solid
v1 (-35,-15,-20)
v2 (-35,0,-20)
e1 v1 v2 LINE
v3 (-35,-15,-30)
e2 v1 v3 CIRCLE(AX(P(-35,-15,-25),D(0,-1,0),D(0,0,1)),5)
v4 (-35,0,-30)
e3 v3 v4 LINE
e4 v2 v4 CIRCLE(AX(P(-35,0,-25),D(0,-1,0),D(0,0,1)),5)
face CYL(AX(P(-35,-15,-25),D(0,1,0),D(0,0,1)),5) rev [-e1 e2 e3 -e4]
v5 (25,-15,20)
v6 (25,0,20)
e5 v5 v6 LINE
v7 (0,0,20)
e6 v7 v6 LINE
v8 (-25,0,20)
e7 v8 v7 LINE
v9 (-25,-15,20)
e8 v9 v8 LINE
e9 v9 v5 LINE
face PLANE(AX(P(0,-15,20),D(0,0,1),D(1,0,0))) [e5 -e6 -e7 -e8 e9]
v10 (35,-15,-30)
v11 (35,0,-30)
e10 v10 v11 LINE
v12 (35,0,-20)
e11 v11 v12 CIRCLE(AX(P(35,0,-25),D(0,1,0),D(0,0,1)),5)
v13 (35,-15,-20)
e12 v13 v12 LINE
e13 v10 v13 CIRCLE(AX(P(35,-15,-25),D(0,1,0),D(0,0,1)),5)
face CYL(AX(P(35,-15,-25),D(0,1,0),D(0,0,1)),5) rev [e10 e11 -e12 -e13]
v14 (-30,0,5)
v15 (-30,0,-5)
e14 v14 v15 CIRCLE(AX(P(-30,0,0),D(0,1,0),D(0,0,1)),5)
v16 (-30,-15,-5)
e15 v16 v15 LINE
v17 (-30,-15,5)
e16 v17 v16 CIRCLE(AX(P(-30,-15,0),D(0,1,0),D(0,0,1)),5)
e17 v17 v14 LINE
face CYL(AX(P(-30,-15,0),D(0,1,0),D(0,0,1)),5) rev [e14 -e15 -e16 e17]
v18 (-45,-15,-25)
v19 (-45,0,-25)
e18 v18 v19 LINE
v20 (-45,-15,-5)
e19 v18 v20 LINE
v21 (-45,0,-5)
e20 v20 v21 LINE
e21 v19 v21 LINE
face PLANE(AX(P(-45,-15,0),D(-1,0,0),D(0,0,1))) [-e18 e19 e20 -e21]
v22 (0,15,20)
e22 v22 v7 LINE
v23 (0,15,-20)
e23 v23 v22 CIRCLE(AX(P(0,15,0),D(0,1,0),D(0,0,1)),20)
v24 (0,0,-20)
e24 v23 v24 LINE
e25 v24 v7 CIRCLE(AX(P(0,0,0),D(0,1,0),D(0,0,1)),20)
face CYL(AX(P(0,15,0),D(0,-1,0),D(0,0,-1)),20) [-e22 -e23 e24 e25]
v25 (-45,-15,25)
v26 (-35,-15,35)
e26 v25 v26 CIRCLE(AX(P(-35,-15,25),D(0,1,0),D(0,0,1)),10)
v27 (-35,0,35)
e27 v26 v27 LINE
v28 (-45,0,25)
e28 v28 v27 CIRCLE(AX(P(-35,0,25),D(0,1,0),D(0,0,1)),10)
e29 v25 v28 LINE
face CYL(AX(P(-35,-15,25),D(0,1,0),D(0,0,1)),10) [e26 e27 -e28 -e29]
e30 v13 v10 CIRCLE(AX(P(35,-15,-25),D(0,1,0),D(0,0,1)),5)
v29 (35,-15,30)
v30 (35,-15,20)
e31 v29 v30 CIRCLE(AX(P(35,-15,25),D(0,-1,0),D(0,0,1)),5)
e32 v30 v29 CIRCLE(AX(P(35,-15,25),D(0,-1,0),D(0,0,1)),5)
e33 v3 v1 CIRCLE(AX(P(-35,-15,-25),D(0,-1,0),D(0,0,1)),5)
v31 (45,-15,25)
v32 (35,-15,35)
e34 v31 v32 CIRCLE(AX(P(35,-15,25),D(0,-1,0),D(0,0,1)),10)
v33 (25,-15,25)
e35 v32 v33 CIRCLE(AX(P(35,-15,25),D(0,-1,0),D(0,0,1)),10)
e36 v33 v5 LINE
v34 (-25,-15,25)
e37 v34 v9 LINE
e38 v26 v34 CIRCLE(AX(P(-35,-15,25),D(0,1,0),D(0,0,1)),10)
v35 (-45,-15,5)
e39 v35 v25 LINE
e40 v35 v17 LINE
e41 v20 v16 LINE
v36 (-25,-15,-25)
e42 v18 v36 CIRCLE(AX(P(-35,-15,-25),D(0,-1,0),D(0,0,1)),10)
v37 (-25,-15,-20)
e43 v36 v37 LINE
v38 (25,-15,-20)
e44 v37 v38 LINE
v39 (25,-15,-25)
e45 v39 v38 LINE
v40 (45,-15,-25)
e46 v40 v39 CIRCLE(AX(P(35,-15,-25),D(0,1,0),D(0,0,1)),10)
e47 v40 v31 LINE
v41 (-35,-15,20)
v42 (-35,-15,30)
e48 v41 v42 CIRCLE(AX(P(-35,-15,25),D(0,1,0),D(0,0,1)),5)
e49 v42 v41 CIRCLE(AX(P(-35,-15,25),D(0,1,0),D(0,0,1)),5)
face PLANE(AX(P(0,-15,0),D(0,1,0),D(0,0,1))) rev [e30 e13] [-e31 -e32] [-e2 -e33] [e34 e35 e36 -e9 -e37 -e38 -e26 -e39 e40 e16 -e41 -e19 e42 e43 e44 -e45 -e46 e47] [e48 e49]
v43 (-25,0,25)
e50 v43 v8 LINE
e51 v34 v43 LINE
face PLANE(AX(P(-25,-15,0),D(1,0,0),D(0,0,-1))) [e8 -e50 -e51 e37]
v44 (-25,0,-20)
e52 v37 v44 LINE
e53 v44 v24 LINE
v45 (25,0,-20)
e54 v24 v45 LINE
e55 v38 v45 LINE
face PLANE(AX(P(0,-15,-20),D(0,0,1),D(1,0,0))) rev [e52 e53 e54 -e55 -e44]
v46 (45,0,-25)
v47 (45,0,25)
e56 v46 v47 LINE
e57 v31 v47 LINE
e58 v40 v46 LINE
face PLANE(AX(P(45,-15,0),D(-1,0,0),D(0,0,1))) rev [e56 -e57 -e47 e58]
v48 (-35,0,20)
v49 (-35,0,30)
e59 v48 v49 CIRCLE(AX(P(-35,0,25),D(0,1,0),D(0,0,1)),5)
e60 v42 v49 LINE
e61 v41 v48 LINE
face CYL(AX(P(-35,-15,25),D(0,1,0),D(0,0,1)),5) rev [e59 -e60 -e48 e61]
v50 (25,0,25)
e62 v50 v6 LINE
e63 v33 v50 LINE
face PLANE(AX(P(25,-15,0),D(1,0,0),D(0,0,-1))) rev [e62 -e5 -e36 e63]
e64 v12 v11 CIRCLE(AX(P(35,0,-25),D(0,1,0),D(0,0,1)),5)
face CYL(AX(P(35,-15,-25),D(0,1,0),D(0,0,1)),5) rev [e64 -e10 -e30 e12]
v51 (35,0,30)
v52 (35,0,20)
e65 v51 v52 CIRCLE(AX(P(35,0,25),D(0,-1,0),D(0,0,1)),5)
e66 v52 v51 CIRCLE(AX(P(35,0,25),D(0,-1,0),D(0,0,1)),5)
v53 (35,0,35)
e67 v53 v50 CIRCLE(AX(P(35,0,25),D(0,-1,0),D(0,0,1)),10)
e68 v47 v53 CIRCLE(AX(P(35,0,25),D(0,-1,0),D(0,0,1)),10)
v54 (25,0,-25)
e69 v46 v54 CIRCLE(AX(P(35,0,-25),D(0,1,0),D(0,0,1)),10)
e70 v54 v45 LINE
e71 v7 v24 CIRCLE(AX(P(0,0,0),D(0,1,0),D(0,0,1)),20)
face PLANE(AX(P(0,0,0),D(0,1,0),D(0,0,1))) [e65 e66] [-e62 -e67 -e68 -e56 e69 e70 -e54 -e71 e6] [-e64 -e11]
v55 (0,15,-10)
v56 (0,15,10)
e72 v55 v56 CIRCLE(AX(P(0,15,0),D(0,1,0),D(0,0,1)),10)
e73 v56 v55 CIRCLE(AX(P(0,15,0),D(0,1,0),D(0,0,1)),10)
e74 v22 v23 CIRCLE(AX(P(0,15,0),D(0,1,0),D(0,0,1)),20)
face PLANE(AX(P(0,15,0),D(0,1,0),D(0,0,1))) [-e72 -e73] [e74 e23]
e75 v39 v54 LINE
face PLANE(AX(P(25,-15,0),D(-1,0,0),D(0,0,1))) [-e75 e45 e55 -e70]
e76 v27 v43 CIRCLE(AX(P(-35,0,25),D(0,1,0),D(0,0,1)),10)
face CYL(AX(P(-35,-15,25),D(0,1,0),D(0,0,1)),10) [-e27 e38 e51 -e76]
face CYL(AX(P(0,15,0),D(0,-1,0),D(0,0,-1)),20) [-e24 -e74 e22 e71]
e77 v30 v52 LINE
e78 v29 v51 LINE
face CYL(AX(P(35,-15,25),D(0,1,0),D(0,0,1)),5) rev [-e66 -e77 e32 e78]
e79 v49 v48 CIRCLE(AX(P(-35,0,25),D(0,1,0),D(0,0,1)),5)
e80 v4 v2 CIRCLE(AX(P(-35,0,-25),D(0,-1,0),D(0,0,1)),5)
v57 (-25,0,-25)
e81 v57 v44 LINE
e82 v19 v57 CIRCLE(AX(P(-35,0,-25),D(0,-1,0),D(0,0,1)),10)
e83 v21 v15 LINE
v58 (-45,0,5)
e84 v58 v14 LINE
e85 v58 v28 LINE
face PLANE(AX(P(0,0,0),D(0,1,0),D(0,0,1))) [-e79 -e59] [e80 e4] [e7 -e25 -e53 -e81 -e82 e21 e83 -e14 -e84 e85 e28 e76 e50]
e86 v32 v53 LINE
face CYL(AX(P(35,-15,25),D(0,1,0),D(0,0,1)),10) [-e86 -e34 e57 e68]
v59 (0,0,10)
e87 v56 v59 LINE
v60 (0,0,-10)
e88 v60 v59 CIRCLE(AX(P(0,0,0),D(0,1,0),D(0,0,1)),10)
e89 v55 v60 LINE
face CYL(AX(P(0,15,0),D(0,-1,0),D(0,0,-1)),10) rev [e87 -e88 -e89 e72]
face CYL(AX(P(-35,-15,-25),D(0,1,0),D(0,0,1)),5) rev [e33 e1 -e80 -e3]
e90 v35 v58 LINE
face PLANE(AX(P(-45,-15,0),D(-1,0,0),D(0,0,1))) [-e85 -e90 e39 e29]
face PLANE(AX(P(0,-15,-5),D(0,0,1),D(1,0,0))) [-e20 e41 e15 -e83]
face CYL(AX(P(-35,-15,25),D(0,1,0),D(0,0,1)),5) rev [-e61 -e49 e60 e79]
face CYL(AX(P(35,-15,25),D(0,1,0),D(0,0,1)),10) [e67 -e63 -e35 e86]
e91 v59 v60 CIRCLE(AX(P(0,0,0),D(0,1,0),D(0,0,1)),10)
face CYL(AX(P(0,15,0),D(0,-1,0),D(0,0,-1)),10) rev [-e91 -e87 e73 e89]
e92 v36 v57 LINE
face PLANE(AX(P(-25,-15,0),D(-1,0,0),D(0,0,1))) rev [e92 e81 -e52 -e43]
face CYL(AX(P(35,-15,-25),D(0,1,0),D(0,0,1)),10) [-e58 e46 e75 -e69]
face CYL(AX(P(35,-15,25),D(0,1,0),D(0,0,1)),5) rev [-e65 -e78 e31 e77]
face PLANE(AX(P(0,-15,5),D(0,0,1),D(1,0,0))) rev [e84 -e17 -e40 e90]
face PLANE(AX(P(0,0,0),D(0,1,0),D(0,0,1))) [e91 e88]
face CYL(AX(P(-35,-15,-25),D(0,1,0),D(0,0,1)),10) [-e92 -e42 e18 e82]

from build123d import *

# Parameters (mm, degrees)
BASE_PLATE_SKETCH_R         = 5
BASE_PLATE_DEPTH            = 15
PIVOT_BOSS_SKETCH_R         = 20
PIVOT_BOSS_SKETCH_R_2       = 10
PIVOT_BOSS_40_BORE_20_DEPTH = 15


with BuildPart() as part:
    # Base Plate Sketch → Base Plate (new body)
    with BuildSketch(Plane(origin=(0, 0, 0), x_dir=(1, 0, 0), z_dir=(0, 1, 0))):
        with BuildLine():
            Line((45, 25), (45, -25))
            ThreePointArc((45, -25), (35, -35), (25, -25))
            Line((25, -25), (25, -20))
            Line((25, -20), (-25, -20))
            Line((-25, -20), (-25, -25))
            ThreePointArc((-25, -25), (-35, -35), (-45, -25))
            Line((-45, -25), (-45, -5))
            Line((-45, -5), (-30, -5))
            ThreePointArc((-30, -5), (-25, 0), (-30, 5))
            Line((-30, 5), (-45, 5))
            Line((-45, 5), (-45, 25))
            ThreePointArc((-45, 25), (-35, 35), (-25, 25))
            Line((-25, 25), (-25, 20))
            Line((-25, 20), (25, 20))
            Line((25, 20), (25, 25))
            ThreePointArc((25, 25), (35, 35), (45, 25))
        make_face()
        with Locations(Location((35, -25, 0), (0, 0, 270))):
            Circle(BASE_PLATE_SKETCH_R, mode=Mode.SUBTRACT)
        with Locations(Location((-35, -25, 0), (0, 0, 270))):
            Circle(BASE_PLATE_SKETCH_R, mode=Mode.SUBTRACT)
        with Locations(Location((35, 25, 0), (0, 0, 270))):
            Circle(BASE_PLATE_SKETCH_R, mode=Mode.SUBTRACT)
        with Locations(Location((-35, 25, 0), (0, 0, 270))):
            Circle(BASE_PLATE_SKETCH_R, mode=Mode.SUBTRACT)
    extrude(amount=-BASE_PLATE_DEPTH)

    # Pivot Boss Sketch → Pivot Boss Ø40 Bore Ø20 (add)
    with BuildSketch(Plane(origin=(0, 0, 0), x_dir=(1, 0, 0), z_dir=(0, 1, 0))):
        with Locations(Location((0, 0, 0), (0, 0, 270))):
            Circle(PIVOT_BOSS_SKETCH_R)
        with Locations(Location((0, 0, 0), (0, 0, 270))):
            Circle(PIVOT_BOSS_SKETCH_R_2, mode=Mode.SUBTRACT)
    extrude(amount=PIVOT_BOSS_40_BORE_20_DEPTH)


solid = part.part
